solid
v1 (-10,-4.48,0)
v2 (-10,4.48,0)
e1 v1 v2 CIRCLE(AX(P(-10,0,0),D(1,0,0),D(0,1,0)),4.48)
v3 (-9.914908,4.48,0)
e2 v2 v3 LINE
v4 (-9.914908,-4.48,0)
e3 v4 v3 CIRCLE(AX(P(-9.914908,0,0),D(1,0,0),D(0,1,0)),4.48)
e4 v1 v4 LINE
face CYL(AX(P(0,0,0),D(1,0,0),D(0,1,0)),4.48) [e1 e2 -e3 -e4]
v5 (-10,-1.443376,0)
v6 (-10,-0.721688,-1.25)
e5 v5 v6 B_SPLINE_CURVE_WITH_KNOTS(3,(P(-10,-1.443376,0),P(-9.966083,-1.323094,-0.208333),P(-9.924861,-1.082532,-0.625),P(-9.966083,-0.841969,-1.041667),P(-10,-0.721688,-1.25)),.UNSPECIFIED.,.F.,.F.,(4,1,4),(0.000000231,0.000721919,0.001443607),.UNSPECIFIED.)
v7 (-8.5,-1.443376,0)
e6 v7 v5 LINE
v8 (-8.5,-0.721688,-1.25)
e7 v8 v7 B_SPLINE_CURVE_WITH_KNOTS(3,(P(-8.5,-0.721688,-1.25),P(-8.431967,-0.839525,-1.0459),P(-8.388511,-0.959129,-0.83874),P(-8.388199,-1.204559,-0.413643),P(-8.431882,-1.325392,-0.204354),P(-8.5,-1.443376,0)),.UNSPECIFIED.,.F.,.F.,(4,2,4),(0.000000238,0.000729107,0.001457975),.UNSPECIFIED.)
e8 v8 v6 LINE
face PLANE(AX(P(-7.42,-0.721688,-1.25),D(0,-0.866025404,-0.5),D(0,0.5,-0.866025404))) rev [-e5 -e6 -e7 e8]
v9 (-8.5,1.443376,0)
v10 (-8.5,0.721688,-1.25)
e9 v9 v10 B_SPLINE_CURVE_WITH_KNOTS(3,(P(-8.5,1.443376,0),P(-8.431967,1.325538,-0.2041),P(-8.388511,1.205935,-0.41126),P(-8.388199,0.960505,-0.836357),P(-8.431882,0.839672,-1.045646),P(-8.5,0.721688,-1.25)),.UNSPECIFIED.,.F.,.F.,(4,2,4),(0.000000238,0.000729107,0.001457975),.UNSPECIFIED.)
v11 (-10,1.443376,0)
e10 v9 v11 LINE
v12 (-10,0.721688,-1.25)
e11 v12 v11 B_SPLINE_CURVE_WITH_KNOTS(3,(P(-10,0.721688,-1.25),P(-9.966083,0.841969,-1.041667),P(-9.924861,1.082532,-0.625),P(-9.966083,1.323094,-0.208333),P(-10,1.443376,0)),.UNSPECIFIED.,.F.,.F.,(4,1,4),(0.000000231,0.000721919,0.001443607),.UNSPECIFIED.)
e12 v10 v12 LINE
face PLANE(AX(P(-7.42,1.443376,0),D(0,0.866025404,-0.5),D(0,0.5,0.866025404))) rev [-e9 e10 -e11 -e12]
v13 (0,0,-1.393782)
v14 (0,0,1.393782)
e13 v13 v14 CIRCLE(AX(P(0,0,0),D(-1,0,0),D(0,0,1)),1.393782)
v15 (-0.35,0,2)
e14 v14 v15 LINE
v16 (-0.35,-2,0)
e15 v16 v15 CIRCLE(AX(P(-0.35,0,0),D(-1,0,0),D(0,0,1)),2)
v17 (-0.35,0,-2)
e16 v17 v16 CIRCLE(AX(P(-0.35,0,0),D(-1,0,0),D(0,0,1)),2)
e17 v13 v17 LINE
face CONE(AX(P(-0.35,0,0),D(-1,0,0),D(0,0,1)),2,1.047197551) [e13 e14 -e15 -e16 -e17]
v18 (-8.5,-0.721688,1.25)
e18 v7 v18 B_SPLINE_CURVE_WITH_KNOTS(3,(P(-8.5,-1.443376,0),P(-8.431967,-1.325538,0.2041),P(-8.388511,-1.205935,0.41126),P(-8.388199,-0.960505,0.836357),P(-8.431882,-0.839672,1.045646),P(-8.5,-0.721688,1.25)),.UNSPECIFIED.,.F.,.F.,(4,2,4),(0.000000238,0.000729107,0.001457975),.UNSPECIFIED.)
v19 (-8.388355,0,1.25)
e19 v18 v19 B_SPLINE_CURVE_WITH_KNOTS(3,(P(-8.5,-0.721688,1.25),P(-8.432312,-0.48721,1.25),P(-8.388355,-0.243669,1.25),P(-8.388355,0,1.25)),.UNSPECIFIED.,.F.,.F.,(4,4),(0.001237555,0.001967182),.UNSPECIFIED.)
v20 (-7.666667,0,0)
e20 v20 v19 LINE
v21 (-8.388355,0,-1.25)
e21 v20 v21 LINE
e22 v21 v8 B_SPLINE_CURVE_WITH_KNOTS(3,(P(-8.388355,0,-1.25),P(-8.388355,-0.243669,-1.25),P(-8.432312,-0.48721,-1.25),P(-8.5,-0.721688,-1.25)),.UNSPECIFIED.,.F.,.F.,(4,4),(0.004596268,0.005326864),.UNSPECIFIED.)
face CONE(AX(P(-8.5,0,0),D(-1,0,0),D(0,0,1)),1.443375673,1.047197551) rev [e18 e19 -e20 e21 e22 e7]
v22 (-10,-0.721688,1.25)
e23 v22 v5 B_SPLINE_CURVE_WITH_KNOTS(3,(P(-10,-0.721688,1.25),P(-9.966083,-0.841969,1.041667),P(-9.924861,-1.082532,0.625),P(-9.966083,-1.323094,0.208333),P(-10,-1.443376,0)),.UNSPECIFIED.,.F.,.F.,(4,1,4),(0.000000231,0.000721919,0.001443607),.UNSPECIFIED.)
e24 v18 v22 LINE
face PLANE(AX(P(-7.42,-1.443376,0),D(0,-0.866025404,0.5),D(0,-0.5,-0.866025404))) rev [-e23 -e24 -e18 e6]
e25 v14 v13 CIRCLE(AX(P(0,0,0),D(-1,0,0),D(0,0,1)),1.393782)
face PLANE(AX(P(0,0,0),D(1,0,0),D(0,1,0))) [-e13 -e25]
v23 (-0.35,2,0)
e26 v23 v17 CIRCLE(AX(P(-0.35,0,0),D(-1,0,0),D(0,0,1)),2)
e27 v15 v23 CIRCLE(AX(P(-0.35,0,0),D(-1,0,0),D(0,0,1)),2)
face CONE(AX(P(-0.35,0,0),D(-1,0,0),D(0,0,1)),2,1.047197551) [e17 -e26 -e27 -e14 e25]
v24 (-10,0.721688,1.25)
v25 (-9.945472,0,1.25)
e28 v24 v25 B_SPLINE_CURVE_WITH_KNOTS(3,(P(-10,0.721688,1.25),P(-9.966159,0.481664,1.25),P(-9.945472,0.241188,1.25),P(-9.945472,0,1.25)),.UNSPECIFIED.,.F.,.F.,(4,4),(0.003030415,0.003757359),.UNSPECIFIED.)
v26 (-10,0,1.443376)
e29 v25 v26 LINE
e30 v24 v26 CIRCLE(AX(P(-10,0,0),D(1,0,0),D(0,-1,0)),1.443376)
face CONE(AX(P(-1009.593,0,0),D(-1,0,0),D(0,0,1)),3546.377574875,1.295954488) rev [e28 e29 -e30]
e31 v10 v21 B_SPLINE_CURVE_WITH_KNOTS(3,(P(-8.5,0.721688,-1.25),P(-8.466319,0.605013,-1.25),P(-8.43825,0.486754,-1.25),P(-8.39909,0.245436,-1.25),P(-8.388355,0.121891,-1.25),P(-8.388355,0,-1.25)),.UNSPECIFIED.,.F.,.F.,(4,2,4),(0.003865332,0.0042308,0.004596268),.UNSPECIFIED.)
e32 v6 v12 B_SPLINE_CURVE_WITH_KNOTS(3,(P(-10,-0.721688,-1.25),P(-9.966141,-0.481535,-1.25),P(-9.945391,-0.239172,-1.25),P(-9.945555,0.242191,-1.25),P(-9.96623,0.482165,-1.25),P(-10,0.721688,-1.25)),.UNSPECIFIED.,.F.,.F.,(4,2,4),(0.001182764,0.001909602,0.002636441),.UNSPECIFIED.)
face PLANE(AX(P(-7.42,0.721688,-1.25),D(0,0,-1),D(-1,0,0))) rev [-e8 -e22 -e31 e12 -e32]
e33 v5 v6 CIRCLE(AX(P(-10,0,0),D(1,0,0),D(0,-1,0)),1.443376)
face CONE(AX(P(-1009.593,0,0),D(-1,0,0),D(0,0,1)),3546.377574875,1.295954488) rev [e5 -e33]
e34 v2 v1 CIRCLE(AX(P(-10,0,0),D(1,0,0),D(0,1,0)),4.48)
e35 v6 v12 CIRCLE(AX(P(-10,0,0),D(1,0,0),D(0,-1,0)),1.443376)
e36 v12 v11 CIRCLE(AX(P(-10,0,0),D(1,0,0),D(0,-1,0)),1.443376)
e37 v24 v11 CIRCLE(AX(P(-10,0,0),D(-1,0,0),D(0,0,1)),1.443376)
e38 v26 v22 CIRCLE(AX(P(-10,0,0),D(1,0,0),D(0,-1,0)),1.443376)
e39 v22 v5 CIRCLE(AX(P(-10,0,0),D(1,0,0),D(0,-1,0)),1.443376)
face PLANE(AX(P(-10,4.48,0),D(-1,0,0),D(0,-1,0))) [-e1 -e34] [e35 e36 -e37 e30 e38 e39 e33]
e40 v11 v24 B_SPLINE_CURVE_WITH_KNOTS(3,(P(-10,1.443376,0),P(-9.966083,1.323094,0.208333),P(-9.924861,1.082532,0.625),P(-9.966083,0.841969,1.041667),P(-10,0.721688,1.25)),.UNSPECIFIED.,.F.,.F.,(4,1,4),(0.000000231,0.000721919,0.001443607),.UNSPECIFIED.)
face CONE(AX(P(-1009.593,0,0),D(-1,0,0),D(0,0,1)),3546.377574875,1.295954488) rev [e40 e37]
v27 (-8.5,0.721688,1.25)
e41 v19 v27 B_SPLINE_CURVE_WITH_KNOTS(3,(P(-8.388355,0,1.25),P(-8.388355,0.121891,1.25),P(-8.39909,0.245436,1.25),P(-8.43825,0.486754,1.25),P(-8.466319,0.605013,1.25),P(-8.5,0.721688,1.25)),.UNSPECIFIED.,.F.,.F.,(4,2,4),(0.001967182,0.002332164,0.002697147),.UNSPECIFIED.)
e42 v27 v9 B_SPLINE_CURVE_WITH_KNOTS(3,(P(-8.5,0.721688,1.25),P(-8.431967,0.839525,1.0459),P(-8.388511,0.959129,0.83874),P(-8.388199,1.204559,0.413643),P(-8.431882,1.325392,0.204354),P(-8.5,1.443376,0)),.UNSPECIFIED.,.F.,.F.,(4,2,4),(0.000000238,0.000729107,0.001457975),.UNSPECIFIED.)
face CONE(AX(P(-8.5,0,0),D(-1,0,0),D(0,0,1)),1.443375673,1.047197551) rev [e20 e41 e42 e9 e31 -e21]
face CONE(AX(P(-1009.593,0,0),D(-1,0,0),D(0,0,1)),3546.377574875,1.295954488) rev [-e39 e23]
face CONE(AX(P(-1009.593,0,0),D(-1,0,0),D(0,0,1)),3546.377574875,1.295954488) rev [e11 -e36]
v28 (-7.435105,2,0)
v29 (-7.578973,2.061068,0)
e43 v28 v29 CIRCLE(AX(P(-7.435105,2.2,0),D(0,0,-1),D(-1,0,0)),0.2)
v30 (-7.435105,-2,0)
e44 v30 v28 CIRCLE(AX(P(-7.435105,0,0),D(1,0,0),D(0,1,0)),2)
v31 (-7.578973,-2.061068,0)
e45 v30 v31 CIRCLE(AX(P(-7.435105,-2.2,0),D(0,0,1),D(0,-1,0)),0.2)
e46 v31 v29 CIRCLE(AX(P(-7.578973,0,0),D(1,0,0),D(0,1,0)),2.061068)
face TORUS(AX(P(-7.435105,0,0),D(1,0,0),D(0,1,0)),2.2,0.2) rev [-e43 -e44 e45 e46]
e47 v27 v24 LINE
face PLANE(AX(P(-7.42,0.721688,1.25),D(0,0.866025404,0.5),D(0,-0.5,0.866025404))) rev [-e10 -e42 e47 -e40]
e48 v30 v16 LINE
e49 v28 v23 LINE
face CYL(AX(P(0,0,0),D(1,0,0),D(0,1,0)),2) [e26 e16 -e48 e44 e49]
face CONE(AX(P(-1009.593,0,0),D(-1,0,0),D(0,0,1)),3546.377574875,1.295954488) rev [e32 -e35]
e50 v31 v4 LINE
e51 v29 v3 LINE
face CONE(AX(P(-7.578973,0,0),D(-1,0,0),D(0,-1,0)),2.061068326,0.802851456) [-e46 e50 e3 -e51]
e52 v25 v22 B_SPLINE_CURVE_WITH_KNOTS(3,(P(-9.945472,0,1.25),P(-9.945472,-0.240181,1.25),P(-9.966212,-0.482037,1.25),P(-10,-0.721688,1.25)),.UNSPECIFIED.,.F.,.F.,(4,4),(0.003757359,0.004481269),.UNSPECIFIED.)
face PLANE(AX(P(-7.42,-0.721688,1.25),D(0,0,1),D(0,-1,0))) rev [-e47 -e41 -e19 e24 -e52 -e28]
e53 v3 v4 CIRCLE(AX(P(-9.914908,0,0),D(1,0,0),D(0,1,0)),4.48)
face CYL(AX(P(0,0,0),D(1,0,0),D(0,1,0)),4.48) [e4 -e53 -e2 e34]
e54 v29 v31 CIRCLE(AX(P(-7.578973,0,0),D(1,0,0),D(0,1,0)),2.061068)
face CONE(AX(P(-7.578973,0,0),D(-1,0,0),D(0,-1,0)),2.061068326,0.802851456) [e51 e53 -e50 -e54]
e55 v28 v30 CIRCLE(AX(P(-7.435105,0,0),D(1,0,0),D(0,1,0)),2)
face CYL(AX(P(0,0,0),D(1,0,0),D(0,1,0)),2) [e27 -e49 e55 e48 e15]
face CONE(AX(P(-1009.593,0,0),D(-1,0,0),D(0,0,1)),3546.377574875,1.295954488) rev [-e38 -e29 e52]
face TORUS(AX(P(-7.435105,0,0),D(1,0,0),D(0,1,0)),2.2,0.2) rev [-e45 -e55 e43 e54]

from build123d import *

# Parameters (mm, degrees)
CUT_EXTRUDE_1_DEPTH = 2.58


with BuildPart() as part:
    # 草图1 → 旋转1 (revolve)
    with BuildSketch(Plane.XY):
        with BuildLine():
            Line((0, 2), (-7.435105037, 2))
            ThreePointArc((-7.435105037, 2), (-7.513251262, 2.015899029), (-7.578972997, 2.061068326))
            Line((-7.578972997, 2.061068326), (-9.914908162, 4.48))
            Line((-9.914908162, 4.48), (-10, 4.48))
            Line((-10, 4.48), (-10, 0))
            Line((-10, 0), (0, 0))
            Line((0, 0), (0, 2))
        make_face()
    revolve(axis=Axis((0, 0, 0), (-1, 0, 0)))

    # 草图2 → 切除-拉伸1 (cut)
    with BuildSketch(Plane.ZY.offset(10)):
        Polygon((0, 1.443375673), (-1.25, 0.721687836), (-1.25, -0.721687836), (0, -1.443375673), (1.25, -0.721687836), (1.25, 0.721687836), align=None)
    extrude(amount=-CUT_EXTRUDE_1_DEPTH, mode=Mode.SUBTRACT)

    # 草图6 → 旋转2 (revolve)
    with BuildSketch(Plane.XY, mode=Mode.PRIVATE) as revolve_2_sk:
        Polygon((-8.5, 1.443375673), (-7.666666667, 0), (-7.05, 0), (-7.05, 1.443375673), align=None)
    revolve(revolve_2_sk.sketch.rotate(Axis((-10, 0, 0), (1, 0, 0)), 90), axis=Axis((-10, 0, 0), (1, 0, 0)))

    # 草图7 → 切除-旋转2 (revolve, cut)
    with BuildSketch(Plane.XY):
        Polygon((-10, 1.443375673), (-10, 0), (-9.593, 0), align=None)
    revolve(axis=Axis((-10, 0, 0), (1, 0, 0)), mode=Mode.SUBTRACT)

    # 草图4 → 切除-旋转1 (revolve, cut)
    with BuildSketch(Plane.XY):
        Polygon((-0.35, 2), (0, 1.393782217), (0.35, 2), align=None)
    revolve(axis=Axis((-0.35, 0, 0), (1, 0, 0)), mode=Mode.SUBTRACT)


solid = part.part
